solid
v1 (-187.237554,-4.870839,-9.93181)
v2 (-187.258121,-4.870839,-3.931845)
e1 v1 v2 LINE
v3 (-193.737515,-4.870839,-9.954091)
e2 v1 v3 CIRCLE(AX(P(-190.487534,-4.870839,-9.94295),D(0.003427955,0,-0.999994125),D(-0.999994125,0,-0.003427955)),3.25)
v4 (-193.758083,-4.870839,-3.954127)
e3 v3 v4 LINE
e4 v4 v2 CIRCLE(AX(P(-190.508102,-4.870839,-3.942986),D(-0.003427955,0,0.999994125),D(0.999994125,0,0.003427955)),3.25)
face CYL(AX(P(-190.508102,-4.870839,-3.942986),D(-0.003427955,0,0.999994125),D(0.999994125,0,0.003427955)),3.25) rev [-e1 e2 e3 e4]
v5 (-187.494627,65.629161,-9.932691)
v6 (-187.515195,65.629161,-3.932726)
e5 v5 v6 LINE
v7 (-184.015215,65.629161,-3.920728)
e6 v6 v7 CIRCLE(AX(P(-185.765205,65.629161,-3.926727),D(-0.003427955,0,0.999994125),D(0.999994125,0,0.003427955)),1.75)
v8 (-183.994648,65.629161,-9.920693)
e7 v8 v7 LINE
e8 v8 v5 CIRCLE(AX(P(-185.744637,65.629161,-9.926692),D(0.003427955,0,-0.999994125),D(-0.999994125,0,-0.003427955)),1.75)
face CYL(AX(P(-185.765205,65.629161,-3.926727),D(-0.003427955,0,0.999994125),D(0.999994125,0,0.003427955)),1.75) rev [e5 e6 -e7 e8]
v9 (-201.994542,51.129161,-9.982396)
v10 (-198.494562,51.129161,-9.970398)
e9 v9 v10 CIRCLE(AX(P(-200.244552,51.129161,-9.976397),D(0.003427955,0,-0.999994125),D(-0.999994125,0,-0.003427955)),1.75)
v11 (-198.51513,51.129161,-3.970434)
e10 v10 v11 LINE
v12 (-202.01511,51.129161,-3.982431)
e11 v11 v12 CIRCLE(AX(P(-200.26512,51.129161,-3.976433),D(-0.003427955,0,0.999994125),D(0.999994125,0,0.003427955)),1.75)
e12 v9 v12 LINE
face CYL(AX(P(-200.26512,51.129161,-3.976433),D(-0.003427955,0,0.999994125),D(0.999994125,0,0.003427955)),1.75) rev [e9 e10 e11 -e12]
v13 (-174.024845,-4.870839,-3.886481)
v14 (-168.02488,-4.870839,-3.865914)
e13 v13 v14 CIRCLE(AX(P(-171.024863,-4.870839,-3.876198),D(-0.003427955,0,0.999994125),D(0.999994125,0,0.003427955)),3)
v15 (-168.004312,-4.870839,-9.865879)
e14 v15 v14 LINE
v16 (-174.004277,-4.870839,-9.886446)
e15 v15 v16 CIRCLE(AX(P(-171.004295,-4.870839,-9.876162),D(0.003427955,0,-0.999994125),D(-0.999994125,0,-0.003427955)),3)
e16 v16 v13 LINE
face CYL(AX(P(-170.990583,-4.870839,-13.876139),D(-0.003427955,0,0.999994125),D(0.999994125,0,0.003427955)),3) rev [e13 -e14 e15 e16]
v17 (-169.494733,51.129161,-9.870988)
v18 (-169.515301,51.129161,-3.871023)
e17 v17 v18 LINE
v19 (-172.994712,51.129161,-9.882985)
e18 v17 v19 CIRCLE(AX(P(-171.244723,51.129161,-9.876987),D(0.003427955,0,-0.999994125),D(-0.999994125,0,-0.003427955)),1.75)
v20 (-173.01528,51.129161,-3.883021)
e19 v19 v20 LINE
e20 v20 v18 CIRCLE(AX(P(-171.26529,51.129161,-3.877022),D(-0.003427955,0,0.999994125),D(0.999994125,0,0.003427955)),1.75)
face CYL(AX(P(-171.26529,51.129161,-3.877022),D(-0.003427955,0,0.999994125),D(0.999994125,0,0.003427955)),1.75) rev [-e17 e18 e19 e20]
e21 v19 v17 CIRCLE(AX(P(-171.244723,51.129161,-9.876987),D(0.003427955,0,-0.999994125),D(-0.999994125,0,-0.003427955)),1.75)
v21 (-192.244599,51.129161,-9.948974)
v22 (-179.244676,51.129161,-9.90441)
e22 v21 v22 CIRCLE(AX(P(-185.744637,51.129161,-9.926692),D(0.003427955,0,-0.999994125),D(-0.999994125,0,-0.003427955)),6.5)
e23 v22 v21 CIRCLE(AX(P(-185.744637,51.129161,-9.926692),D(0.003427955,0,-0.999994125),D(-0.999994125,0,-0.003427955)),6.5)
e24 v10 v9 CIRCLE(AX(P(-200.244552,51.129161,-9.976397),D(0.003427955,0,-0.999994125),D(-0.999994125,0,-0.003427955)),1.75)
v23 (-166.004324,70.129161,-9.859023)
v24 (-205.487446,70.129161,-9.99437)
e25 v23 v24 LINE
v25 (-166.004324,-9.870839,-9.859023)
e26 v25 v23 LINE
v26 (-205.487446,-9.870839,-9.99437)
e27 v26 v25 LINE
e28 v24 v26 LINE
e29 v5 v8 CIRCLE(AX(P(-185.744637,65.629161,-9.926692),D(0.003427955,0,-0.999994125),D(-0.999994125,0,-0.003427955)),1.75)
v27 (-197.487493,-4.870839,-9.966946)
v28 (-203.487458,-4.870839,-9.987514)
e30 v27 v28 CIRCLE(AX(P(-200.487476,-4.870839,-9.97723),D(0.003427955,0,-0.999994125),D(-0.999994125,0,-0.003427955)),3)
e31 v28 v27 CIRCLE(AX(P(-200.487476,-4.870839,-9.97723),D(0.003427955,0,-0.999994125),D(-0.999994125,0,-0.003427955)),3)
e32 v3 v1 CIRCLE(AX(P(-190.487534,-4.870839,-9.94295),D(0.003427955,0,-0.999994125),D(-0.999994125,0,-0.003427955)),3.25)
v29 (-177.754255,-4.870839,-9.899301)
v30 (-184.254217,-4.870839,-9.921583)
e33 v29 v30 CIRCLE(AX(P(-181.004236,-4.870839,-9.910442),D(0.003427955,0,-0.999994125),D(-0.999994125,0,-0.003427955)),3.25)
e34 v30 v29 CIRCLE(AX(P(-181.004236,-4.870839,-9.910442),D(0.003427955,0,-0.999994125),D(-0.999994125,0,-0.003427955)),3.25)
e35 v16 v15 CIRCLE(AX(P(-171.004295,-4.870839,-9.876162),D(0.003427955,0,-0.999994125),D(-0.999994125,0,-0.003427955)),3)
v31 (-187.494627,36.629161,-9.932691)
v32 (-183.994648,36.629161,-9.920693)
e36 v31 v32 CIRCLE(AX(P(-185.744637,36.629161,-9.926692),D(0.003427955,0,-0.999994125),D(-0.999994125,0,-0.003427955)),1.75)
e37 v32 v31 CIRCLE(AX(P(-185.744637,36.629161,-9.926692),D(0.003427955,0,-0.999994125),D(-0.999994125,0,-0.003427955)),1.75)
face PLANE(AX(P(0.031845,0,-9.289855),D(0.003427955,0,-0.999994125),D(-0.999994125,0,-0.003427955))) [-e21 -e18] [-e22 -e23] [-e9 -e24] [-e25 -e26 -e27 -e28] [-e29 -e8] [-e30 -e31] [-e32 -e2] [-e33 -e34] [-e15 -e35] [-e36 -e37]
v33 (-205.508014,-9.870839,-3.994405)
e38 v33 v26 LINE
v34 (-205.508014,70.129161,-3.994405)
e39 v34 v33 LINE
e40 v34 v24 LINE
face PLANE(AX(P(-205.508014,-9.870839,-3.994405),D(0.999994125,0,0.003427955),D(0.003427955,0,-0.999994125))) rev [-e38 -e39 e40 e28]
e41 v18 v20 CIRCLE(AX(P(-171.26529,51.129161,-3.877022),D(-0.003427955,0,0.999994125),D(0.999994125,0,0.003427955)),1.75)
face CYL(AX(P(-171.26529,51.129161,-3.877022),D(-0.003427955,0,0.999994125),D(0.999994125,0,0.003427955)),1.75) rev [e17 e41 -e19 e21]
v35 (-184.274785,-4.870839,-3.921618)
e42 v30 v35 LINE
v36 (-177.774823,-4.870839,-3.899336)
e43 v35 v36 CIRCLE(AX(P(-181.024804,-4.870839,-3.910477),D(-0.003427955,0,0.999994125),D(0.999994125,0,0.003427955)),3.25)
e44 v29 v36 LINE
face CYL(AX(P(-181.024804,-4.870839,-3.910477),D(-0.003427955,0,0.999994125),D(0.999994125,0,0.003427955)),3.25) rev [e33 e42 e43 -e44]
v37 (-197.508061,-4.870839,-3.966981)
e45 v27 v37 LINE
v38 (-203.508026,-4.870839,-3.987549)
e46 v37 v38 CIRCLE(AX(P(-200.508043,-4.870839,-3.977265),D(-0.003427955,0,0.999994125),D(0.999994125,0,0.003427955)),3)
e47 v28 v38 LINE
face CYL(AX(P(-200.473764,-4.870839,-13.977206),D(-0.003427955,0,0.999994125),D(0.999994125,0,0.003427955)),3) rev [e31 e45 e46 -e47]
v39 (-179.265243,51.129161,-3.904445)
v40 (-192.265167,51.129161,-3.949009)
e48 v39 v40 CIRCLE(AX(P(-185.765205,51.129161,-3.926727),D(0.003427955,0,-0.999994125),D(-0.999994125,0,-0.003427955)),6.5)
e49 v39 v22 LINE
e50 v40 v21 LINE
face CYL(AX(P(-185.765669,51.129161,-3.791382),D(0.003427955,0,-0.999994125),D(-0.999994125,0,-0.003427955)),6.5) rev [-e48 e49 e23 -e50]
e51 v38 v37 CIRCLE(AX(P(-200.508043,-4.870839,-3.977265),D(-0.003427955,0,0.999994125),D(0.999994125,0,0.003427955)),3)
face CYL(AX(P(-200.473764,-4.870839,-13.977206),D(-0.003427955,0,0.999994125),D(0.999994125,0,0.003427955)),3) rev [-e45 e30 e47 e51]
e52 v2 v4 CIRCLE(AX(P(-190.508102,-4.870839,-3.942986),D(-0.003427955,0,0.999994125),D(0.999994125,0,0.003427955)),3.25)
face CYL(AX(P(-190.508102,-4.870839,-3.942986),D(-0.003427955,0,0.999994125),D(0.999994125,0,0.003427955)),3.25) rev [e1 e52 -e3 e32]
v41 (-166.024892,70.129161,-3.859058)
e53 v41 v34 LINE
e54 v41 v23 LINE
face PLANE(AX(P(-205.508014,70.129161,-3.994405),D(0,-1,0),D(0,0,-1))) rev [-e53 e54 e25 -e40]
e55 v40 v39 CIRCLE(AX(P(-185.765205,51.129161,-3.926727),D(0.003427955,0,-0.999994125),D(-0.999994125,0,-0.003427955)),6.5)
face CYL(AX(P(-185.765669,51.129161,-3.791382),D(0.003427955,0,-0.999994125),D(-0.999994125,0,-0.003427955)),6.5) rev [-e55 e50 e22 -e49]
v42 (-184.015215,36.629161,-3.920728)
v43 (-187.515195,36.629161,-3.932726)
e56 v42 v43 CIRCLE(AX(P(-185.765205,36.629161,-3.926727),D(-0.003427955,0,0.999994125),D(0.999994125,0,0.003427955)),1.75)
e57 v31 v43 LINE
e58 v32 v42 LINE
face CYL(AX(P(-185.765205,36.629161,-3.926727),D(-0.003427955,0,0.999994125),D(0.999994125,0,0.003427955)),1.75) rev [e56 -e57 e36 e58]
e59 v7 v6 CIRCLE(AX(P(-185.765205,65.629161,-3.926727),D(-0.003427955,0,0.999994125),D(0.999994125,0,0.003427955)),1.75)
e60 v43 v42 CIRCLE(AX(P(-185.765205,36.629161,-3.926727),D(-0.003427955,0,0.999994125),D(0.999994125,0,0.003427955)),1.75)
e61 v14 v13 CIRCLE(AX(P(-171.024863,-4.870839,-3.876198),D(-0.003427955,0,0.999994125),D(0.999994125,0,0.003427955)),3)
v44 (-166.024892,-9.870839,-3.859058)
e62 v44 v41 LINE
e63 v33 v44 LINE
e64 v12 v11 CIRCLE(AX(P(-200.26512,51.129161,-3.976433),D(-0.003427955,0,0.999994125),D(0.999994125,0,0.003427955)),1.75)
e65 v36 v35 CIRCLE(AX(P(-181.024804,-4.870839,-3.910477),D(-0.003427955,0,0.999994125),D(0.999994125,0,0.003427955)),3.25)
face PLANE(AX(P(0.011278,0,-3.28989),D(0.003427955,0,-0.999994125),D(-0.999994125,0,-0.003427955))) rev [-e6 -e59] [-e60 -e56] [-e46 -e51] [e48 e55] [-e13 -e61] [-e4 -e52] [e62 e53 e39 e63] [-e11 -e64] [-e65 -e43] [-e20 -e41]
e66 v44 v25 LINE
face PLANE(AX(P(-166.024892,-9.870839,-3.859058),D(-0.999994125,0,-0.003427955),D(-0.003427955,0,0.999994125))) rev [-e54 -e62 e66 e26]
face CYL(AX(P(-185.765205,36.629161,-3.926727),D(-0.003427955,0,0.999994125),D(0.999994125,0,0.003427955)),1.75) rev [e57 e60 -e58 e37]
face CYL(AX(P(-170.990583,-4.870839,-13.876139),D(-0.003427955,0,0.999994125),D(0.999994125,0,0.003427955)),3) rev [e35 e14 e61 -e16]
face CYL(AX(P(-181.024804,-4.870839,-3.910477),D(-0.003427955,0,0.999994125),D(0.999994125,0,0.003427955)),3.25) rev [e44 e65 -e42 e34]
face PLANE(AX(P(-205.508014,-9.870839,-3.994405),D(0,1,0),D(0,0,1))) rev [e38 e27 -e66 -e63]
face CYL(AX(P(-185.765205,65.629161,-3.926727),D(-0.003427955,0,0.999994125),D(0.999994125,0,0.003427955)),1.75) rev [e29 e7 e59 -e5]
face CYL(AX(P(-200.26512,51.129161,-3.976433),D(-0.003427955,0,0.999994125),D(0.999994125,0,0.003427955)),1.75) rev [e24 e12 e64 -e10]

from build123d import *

# Parameters (mm, degrees)
SKETCH_2_W            = 39.483354071
SKETCH_2_H            = 80
EXTRUDE_1_DEPTH       = 6
SKETCH_3_R            = 3
CUT_EXTRUDE_1_DEPTH   = 10
HOLE_WIZARD_1_0_1_1_D = 6.5
SKETCH_6_R            = 6.5
CUT_EXTRUDE_2_DEPTH   = 218.242322412
HOLE_WIZARD_1_0_1_2_D = 3.5


with BuildPart() as part:
    # 草图2 → 凸台-拉伸1 (new body)
    with BuildSketch(Plane(origin=(0.031845394, 0, -9.289854674), x_dir=(0.9999941245437004, 0, 0.0034279553787324732), z_dir=(-0.0034279553787324732, 0, 0.9999941245437004))):
        with Locations((-185.77882216, 30.129161482)):
            Rectangle(SKETCH_2_W, SKETCH_2_H)
    extrude(amount=EXTRUDE_1_DEPTH)

    # 草图3 → 切除-拉伸1 (cut)
    with BuildSketch(Plane(origin=(0.011277662, 0, -3.289889926), x_dir=(0.9999941245437003, 0, 0.003427955378732479), z_dir=(-0.003427955378732479, 0, 0.9999941245437004))):
        with Locations((-200.520499196, -4.870838518)):
            Circle(SKETCH_3_R)
        with Locations((-171.037145125, -4.870838518)):
            Circle(SKETCH_3_R)
    extrude(amount=-CUT_EXTRUDE_1_DEPTH, mode=Mode.SUBTRACT)

    # Ø1.0 (1) 直径孔1 (through all)
    with Locations(Plane(origin=(0.011277662, 0, -3.289889926), x_dir=(0.9999941245437003, 0, 0.003427955378732479), z_dir=(-0.003427955378732479, 0, 0.9999941245437004))):
        with Locations((-190.520499196, -4.870838518), (-181.037145125, -4.870838518)):
            Hole(HOLE_WIZARD_1_0_1_1_D / 2)

    # 草图6 → 切除-拉伸2 (cut, through all)
    with BuildSketch(Plane(origin=(0.031845394, 0, -9.289854674), x_dir=(-0.9999941245437003, 0, -0.003427955378732479), z_dir=(0.003427955378732479, 0, -0.9999941245437004))):
        with Locations((185.777574302, 51.129161482)):
            Circle(SKETCH_6_R)
    extrude(amount=-CUT_EXTRUDE_2_DEPTH, mode=Mode.SUBTRACT)

    # Ø1.0 (1) 直径孔2 (through all)
    with Locations(Plane(origin=(0.011277662, 0, -3.289889926), x_dir=(0.9999941245437003, 0, 0.003427955378732479), z_dir=(-0.003427955378732479, 0, 0.9999941245437004))):
        with Locations((-185.777574302, 65.629161482), (-171.277574302, 51.129161482), (-185.777574302, 36.629161482), (-200.277574302, 51.129161482)):
            Hole(HOLE_WIZARD_1_0_1_2_D / 2)


solid = part.part
